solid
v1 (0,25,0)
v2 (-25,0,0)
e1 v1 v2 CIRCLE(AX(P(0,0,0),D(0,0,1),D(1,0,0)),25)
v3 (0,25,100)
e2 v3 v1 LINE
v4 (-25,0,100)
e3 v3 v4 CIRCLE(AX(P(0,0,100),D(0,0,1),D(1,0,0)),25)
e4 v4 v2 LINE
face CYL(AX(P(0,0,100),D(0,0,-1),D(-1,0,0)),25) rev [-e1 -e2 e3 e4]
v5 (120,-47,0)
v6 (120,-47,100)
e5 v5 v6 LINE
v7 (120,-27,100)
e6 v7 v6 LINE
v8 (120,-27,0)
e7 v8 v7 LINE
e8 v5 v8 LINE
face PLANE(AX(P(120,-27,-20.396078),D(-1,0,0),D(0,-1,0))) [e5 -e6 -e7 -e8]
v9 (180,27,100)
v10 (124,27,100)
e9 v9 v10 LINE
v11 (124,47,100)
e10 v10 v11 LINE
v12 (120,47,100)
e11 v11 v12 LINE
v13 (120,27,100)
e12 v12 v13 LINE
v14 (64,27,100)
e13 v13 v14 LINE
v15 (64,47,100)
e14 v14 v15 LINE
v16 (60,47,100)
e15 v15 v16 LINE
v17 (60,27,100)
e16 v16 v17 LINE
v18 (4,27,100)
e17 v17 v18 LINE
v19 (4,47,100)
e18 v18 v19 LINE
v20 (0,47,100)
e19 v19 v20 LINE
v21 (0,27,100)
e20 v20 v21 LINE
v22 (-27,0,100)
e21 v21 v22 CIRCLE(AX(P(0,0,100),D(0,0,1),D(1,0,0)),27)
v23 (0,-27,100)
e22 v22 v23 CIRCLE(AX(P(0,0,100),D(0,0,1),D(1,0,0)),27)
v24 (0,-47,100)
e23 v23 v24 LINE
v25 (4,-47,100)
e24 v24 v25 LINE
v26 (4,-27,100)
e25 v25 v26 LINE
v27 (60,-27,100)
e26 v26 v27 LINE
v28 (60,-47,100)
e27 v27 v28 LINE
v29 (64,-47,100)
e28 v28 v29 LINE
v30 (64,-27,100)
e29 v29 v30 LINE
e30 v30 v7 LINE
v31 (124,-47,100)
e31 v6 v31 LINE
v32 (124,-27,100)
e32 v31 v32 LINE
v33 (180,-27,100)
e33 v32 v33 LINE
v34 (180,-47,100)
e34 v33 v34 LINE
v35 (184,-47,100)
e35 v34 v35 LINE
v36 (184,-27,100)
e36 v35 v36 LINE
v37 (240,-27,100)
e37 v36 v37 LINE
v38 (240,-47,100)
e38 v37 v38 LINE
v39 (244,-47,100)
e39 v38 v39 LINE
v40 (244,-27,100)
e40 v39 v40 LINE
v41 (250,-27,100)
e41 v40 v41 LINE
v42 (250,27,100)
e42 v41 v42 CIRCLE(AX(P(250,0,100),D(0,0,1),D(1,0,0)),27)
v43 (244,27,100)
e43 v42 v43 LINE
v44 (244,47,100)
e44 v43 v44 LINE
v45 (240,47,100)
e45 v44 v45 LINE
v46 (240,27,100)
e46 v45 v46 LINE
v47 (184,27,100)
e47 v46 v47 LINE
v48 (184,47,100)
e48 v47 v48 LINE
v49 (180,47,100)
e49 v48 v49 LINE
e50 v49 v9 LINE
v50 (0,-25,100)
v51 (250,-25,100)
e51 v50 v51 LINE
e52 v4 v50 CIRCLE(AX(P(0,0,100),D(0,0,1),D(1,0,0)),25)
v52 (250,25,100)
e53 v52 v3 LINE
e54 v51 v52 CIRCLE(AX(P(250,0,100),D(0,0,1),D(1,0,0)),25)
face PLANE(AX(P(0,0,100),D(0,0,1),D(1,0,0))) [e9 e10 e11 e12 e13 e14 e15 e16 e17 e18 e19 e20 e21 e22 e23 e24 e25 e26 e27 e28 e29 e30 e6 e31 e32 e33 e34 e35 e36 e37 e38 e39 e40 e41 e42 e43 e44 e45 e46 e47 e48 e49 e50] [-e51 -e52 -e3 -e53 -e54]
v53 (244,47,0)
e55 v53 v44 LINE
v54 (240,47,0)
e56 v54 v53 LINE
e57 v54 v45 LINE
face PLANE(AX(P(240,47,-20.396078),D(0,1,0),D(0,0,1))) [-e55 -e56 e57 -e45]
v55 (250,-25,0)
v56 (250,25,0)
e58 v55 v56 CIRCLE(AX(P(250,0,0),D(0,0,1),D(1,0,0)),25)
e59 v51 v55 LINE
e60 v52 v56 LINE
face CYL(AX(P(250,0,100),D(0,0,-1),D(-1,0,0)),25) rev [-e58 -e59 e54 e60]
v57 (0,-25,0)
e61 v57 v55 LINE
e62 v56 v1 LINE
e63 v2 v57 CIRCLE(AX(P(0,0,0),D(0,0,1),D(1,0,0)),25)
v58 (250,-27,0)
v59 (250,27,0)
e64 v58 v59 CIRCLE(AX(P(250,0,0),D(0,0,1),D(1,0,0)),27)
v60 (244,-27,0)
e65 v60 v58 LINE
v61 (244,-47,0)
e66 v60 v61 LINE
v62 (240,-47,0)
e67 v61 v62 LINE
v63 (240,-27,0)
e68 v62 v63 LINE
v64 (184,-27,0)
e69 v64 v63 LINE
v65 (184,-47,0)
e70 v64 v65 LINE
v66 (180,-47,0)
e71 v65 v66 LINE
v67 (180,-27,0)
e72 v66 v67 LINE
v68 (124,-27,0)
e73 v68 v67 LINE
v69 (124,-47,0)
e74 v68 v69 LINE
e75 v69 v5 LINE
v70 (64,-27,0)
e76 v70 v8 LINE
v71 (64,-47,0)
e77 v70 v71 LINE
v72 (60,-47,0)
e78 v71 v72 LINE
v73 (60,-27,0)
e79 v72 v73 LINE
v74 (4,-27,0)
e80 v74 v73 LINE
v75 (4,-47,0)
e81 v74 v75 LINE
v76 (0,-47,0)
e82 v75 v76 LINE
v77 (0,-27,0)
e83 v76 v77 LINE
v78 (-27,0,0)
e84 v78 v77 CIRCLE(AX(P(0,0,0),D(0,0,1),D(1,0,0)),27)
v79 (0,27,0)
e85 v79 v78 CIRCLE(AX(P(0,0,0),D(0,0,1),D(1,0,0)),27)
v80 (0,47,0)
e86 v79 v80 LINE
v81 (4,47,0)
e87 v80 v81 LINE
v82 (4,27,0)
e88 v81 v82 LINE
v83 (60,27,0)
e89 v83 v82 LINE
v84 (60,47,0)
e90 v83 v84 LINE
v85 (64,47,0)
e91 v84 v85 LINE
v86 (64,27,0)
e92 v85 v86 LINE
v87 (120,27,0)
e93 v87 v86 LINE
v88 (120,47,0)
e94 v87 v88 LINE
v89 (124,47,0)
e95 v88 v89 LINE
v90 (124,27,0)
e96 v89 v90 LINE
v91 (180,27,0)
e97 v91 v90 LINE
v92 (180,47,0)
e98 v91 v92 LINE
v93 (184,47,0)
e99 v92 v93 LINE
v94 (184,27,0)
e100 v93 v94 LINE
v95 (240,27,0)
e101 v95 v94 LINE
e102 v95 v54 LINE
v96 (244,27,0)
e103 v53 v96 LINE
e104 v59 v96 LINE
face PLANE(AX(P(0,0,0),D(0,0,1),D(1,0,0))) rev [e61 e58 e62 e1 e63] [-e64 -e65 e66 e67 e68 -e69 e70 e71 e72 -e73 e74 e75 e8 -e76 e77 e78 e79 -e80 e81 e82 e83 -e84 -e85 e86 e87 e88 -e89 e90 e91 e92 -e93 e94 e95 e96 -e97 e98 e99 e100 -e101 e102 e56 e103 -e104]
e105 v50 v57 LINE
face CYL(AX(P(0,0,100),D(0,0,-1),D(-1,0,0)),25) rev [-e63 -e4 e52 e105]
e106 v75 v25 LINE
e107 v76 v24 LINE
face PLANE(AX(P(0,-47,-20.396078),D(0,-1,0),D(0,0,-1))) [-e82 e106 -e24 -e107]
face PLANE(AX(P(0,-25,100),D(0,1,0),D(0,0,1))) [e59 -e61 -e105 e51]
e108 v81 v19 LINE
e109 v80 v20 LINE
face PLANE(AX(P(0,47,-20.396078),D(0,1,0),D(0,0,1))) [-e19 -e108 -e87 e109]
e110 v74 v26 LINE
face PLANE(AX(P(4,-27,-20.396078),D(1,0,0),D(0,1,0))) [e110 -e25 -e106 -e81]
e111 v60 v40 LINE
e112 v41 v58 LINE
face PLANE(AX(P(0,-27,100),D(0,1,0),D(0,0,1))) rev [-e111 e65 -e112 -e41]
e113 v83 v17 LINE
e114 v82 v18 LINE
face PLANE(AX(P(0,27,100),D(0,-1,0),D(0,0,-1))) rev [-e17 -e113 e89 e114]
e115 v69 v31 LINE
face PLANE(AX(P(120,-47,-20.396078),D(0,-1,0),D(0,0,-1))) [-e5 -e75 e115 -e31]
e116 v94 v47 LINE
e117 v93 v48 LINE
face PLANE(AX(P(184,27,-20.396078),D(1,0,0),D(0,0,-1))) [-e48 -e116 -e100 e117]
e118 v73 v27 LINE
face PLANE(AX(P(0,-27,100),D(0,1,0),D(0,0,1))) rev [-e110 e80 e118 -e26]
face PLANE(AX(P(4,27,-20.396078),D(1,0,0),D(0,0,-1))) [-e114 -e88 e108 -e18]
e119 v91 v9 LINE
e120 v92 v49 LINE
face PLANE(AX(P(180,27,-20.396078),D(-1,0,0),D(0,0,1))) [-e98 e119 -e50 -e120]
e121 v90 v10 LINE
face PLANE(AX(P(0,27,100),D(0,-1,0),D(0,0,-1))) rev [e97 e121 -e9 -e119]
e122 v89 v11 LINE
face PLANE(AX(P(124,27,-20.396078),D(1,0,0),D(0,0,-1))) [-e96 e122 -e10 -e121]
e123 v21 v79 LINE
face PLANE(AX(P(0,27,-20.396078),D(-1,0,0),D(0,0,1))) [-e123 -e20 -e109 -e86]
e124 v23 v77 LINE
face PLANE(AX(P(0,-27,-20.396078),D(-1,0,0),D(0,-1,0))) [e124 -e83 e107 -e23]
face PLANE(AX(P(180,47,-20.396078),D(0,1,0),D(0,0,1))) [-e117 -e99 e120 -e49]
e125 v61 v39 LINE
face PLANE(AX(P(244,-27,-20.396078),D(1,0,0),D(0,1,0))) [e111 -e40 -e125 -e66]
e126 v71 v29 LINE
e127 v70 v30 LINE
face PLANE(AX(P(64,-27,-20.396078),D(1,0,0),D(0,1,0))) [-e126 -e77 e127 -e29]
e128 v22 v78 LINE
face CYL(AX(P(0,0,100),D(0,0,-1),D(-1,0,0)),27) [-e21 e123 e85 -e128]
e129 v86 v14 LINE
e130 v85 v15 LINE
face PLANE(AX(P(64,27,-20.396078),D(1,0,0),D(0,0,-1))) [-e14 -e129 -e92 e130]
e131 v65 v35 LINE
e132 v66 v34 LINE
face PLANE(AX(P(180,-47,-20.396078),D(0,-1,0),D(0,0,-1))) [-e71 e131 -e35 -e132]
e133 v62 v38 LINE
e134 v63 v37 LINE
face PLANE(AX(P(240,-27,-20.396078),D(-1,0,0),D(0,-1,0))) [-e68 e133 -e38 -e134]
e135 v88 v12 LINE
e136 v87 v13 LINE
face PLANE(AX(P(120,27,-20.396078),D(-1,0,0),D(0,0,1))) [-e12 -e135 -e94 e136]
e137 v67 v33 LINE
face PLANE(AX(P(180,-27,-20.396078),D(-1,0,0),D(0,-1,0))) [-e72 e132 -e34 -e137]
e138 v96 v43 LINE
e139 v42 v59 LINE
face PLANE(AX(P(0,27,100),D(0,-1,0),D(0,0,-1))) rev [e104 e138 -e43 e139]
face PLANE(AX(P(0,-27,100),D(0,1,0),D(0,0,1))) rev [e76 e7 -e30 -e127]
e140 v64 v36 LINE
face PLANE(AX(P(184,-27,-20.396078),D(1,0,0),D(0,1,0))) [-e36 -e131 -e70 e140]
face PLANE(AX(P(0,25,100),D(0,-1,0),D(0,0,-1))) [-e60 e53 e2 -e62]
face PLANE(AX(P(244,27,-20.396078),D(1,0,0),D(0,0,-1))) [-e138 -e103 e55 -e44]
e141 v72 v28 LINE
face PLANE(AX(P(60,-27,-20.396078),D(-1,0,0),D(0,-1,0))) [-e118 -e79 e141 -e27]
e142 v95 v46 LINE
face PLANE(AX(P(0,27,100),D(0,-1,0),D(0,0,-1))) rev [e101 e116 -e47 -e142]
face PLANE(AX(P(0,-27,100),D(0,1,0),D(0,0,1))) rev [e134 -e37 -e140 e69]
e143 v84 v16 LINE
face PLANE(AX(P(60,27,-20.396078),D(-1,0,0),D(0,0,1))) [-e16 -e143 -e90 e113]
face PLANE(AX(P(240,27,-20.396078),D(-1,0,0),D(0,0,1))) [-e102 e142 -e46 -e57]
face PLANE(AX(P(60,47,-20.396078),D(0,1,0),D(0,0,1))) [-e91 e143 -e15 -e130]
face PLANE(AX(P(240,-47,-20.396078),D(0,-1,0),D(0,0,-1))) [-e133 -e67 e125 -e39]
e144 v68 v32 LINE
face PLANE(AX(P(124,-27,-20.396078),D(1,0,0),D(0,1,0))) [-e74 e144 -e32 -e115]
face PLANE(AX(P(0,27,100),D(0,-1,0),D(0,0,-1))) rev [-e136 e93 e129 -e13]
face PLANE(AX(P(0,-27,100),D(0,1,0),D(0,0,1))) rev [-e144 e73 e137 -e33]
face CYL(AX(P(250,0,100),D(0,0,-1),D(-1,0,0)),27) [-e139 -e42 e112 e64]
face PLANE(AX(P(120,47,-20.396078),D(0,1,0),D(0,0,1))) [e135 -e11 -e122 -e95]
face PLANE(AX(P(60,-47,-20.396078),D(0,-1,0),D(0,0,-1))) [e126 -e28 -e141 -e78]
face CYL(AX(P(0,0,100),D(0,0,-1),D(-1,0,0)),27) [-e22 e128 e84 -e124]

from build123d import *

# Parameters (mm, degrees)
EXTRUDE_1_DEPTH        = 100
SKETCH_2_W             = 4
SKETCH_2_H             = 20
EXTRUDE_2_DEPTH        = 100
PATTERN_LINEAR_1_COUNT = 5
PATTERN_LINEAR_1_PITCH = 60
SKETCH_3_W             = 4
SKETCH_3_H             = 20
EXTRUDE_3_DEPTH        = 100
PATTERN_LINEAR_2_COUNT = 5
PATTERN_LINEAR_2_PITCH = 60


with BuildPart() as part:
    # 草图1 → 凸台-拉伸1 (new body)
    with BuildSketch(Plane.XY):
        with BuildLine():
            Line((0, 27), (250, 27))
            ThreePointArc((250, 27), (277, 0), (250, -27))
            Line((250, -27), (0, -27))
            ThreePointArc((0, -27), (-27, 0), (0, 27))
        make_face()
        with BuildLine():
            Line((0, 25), (250, 25))
            ThreePointArc((250, 25), (275, 0), (250, -25))
            Line((250, -25), (0, -25))
            ThreePointArc((0, -25), (-25, 0), (0, 25))
        make_face(mode=Mode.SUBTRACT)
    extrude(amount=EXTRUDE_1_DEPTH)

    # 草图2 → 凸台-拉伸2 (add)
    with BuildSketch(Plane.XY.offset(100)):
        with Locations((2, 37)):
            Rectangle(SKETCH_2_W, SKETCH_2_H)
    extrude_2 = extrude(amount=-EXTRUDE_2_DEPTH)

    # 阵列(线性)1: 凸台-拉伸2 ×5
    with Locations(*[(i * PATTERN_LINEAR_1_PITCH, 0, 0) for i in range(1, PATTERN_LINEAR_1_COUNT)]):
        add(extrude_2)

    # 草图3 → 凸台-拉伸3 (add)
    with BuildSketch(Plane.XY.offset(100)):
        with Locations((2, -37)):
            Rectangle(SKETCH_3_W, SKETCH_3_H)
    extrude_3 = extrude(amount=-EXTRUDE_3_DEPTH)

    # 阵列(线性)2: 凸台-拉伸3 ×5
    with Locations(*[(i * PATTERN_LINEAR_2_PITCH, 0, 0) for i in range(1, PATTERN_LINEAR_2_COUNT)]):
        add(extrude_3)


solid = part.part
